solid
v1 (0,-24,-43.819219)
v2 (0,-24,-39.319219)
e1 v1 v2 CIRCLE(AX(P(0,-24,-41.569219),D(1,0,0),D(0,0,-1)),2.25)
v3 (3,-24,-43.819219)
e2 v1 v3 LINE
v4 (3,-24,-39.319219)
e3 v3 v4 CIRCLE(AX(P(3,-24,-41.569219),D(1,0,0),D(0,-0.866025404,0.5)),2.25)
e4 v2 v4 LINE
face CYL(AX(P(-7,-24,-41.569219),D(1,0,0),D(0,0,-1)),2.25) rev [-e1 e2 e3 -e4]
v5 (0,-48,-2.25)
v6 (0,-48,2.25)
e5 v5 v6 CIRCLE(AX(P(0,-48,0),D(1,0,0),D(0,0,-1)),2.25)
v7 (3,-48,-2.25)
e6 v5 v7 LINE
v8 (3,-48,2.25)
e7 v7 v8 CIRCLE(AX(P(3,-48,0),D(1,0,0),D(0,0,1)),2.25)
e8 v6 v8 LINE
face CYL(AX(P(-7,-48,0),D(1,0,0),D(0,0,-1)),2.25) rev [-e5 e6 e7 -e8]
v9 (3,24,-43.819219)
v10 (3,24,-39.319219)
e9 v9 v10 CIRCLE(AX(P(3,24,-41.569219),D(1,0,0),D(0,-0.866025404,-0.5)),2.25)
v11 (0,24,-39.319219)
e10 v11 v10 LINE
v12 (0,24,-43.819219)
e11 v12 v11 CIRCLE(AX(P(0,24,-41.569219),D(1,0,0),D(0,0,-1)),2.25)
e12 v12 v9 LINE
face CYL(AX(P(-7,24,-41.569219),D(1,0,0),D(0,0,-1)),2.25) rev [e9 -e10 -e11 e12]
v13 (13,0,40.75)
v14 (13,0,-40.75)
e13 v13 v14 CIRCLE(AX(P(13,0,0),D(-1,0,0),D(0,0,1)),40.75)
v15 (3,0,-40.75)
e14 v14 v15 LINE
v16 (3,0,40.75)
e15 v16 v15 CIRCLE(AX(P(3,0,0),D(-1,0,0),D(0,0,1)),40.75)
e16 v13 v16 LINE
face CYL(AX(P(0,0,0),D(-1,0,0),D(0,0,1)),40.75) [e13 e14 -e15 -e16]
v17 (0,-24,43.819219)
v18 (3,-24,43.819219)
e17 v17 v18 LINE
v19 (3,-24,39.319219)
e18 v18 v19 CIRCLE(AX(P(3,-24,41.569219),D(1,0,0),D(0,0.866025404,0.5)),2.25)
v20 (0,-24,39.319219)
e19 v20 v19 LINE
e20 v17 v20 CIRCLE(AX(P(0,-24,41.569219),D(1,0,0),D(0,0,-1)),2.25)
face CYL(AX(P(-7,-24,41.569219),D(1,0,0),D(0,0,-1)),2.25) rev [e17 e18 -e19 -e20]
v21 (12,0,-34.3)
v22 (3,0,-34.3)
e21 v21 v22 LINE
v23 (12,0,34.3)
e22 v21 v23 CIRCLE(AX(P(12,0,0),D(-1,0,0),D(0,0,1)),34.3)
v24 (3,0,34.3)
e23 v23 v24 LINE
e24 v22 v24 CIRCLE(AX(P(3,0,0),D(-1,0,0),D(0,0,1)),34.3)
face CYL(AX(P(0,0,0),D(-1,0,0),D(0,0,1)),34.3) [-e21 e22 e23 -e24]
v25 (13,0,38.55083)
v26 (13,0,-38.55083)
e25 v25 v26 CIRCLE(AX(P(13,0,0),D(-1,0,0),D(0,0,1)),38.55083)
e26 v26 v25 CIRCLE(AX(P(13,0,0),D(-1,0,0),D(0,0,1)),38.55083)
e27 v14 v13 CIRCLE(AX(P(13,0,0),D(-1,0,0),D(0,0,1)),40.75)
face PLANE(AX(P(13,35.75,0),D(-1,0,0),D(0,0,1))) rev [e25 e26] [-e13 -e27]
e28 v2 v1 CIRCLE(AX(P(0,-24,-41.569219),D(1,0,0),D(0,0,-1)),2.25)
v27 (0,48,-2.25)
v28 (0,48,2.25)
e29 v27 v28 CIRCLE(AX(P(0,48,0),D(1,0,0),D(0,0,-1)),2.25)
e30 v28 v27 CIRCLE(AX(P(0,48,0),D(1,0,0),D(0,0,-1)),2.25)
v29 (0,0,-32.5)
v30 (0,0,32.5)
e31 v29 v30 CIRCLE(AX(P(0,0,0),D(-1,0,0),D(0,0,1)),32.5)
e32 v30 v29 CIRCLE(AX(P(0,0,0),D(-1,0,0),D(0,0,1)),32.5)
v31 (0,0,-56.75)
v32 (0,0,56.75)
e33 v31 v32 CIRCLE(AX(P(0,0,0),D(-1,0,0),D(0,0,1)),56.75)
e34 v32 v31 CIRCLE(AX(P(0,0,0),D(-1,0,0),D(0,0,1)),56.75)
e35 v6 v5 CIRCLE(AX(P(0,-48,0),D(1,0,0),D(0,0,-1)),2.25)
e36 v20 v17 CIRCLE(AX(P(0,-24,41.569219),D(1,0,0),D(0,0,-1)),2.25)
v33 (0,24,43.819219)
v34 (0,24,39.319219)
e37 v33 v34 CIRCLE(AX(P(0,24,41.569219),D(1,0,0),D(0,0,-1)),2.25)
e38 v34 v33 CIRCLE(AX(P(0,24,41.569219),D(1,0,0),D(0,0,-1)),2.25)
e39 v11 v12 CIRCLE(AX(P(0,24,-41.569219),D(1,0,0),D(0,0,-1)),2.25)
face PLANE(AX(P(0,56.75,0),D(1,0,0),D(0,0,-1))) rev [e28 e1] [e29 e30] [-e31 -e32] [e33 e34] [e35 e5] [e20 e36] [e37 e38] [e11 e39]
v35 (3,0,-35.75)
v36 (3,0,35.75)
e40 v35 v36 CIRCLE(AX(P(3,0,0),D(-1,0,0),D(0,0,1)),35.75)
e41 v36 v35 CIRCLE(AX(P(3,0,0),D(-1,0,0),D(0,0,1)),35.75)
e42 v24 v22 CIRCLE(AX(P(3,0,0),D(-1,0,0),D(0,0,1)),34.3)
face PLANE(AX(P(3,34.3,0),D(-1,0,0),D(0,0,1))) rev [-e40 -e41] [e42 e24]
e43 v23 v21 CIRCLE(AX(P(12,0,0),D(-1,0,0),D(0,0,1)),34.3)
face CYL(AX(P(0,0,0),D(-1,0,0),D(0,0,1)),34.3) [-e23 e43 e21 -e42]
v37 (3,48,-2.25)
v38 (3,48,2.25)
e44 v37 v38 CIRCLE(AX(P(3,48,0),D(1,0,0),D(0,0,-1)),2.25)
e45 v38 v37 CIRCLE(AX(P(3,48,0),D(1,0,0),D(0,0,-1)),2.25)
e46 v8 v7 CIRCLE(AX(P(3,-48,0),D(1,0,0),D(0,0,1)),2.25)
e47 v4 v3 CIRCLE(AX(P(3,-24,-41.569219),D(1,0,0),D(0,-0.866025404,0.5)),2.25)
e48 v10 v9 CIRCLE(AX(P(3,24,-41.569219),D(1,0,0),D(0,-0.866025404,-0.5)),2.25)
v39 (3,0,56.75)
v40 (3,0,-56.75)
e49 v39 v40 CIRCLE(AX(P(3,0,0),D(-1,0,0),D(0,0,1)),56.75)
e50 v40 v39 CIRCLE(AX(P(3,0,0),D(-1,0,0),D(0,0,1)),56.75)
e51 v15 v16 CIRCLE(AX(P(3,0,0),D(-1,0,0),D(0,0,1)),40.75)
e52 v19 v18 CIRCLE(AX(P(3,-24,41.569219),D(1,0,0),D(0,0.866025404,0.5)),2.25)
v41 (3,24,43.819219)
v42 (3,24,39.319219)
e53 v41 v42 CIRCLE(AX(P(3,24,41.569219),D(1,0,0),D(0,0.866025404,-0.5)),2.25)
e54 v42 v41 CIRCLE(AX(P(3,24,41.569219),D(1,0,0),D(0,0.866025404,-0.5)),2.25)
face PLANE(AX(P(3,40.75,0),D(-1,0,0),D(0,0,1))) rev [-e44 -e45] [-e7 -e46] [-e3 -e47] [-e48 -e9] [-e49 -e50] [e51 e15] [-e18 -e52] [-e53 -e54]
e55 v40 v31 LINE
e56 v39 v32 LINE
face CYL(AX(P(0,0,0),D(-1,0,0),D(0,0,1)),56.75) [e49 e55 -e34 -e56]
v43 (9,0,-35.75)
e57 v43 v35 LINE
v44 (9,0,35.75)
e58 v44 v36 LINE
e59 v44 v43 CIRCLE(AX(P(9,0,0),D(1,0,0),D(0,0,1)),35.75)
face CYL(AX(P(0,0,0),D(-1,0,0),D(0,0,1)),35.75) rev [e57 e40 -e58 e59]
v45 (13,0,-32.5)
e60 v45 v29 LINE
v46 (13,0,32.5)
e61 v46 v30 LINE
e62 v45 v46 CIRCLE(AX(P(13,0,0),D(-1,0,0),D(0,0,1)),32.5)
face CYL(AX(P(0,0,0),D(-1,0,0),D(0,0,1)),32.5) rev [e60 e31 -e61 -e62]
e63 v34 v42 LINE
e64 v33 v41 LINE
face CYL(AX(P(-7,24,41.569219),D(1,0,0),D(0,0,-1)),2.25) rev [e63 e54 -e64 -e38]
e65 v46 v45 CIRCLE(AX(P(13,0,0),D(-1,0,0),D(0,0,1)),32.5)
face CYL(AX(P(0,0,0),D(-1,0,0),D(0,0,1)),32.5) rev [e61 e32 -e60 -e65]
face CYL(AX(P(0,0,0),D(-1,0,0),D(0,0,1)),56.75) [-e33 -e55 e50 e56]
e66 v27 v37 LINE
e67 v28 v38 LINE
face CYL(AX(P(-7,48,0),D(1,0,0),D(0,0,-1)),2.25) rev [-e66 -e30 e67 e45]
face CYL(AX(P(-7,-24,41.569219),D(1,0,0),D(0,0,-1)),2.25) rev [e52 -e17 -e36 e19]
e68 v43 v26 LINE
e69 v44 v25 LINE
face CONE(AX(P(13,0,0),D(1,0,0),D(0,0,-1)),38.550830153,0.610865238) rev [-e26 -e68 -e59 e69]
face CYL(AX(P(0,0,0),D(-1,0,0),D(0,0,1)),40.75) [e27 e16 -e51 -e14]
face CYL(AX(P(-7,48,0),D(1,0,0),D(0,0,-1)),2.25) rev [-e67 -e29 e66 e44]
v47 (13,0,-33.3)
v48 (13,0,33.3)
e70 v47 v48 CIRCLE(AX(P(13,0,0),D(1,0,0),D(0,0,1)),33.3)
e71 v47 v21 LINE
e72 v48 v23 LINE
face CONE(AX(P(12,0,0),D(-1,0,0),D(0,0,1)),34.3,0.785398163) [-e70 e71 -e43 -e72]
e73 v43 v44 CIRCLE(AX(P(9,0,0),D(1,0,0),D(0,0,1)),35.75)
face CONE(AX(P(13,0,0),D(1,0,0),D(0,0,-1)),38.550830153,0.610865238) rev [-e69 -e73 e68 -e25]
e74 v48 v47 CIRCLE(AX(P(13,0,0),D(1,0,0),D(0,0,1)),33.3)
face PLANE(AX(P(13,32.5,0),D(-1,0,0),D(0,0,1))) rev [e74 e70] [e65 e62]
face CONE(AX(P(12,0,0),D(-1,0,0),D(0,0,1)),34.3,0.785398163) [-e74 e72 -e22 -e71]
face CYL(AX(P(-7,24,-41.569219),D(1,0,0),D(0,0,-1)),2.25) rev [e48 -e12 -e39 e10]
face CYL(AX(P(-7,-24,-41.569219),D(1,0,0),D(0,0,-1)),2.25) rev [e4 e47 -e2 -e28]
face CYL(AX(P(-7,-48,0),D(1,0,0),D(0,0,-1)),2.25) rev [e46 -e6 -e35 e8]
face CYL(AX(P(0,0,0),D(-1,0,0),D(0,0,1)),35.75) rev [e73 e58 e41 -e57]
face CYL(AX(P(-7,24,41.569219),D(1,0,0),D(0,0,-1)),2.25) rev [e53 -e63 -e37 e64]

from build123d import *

# Parameters (mm, degrees)
CHAMFER1_SIZE      = 4
CHAMFER1_SIZE2     = 2.800830153
CHAMFER2_SIZE      = 1
SKETCH2_R          = 2.25
CUT_EXTRUDE1_DEPTH = 10
CIRPATTERN1_COUNT  = 6


with BuildPart() as part:
    # Sketch1 → Revolve1 (revolve)
    with BuildSketch(Plane.XY, mode=Mode.PRIVATE) as revolve1_sk:
        Polygon((0, 32.5), (13, 32.5), (13, 34.3), (3, 34.3), (3, 35.75), (13, 35.75), (13, 40.75), (3, 40.75), (3, 56.75), (0, 56.75), align=None)
    revolve(revolve1_sk.sketch.rotate(Axis((0, 0, 0), (1, 0, 0)), 90), axis=Axis((0, 0, 0), (1, 0, 0)))

    # Chamfer1
    chamfer1_edges = [part.edges().sort_by_distance(p)[0] for p in [
        (13, 0, -35.75),
    ]]
    chamfer1_side = [part.faces().sort_by_distance(p)[0] for p in [
        (8, 0, -35.75),
    ]]
    chamfer(chamfer1_edges, length=CHAMFER1_SIZE, length2=CHAMFER1_SIZE2, reference=chamfer1_side[0])

    # Chamfer2
    chamfer2_edges = [part.edges().sort_by_distance(p)[0] for p in [
        (13, 0, -34.3),
    ]]
    chamfer(chamfer2_edges, length=CHAMFER2_SIZE)

    # Sketch2 → Cut-Extrude1 (cut)
    with BuildSketch(Plane(origin=(3, 0, 0), x_dir=(0, 0, -1), z_dir=(1, 0, 0))):
        with Locations((0, 48)):
            Circle(SKETCH2_R)
    cut_extrude1 = extrude(amount=-CUT_EXTRUDE1_DEPTH, mode=Mode.SUBTRACT)

    # CirPattern1: Cut-Extrude1 ×6 about axis
    cirpattern1_axis = Axis((0, 0, 0), (1, 0, 0))
    for i in range(1, CIRPATTERN1_COUNT):
        add(cut_extrude1.rotate(cirpattern1_axis, i * 360 / CIRPATTERN1_COUNT), mode=Mode.SUBTRACT)


solid = part.part
